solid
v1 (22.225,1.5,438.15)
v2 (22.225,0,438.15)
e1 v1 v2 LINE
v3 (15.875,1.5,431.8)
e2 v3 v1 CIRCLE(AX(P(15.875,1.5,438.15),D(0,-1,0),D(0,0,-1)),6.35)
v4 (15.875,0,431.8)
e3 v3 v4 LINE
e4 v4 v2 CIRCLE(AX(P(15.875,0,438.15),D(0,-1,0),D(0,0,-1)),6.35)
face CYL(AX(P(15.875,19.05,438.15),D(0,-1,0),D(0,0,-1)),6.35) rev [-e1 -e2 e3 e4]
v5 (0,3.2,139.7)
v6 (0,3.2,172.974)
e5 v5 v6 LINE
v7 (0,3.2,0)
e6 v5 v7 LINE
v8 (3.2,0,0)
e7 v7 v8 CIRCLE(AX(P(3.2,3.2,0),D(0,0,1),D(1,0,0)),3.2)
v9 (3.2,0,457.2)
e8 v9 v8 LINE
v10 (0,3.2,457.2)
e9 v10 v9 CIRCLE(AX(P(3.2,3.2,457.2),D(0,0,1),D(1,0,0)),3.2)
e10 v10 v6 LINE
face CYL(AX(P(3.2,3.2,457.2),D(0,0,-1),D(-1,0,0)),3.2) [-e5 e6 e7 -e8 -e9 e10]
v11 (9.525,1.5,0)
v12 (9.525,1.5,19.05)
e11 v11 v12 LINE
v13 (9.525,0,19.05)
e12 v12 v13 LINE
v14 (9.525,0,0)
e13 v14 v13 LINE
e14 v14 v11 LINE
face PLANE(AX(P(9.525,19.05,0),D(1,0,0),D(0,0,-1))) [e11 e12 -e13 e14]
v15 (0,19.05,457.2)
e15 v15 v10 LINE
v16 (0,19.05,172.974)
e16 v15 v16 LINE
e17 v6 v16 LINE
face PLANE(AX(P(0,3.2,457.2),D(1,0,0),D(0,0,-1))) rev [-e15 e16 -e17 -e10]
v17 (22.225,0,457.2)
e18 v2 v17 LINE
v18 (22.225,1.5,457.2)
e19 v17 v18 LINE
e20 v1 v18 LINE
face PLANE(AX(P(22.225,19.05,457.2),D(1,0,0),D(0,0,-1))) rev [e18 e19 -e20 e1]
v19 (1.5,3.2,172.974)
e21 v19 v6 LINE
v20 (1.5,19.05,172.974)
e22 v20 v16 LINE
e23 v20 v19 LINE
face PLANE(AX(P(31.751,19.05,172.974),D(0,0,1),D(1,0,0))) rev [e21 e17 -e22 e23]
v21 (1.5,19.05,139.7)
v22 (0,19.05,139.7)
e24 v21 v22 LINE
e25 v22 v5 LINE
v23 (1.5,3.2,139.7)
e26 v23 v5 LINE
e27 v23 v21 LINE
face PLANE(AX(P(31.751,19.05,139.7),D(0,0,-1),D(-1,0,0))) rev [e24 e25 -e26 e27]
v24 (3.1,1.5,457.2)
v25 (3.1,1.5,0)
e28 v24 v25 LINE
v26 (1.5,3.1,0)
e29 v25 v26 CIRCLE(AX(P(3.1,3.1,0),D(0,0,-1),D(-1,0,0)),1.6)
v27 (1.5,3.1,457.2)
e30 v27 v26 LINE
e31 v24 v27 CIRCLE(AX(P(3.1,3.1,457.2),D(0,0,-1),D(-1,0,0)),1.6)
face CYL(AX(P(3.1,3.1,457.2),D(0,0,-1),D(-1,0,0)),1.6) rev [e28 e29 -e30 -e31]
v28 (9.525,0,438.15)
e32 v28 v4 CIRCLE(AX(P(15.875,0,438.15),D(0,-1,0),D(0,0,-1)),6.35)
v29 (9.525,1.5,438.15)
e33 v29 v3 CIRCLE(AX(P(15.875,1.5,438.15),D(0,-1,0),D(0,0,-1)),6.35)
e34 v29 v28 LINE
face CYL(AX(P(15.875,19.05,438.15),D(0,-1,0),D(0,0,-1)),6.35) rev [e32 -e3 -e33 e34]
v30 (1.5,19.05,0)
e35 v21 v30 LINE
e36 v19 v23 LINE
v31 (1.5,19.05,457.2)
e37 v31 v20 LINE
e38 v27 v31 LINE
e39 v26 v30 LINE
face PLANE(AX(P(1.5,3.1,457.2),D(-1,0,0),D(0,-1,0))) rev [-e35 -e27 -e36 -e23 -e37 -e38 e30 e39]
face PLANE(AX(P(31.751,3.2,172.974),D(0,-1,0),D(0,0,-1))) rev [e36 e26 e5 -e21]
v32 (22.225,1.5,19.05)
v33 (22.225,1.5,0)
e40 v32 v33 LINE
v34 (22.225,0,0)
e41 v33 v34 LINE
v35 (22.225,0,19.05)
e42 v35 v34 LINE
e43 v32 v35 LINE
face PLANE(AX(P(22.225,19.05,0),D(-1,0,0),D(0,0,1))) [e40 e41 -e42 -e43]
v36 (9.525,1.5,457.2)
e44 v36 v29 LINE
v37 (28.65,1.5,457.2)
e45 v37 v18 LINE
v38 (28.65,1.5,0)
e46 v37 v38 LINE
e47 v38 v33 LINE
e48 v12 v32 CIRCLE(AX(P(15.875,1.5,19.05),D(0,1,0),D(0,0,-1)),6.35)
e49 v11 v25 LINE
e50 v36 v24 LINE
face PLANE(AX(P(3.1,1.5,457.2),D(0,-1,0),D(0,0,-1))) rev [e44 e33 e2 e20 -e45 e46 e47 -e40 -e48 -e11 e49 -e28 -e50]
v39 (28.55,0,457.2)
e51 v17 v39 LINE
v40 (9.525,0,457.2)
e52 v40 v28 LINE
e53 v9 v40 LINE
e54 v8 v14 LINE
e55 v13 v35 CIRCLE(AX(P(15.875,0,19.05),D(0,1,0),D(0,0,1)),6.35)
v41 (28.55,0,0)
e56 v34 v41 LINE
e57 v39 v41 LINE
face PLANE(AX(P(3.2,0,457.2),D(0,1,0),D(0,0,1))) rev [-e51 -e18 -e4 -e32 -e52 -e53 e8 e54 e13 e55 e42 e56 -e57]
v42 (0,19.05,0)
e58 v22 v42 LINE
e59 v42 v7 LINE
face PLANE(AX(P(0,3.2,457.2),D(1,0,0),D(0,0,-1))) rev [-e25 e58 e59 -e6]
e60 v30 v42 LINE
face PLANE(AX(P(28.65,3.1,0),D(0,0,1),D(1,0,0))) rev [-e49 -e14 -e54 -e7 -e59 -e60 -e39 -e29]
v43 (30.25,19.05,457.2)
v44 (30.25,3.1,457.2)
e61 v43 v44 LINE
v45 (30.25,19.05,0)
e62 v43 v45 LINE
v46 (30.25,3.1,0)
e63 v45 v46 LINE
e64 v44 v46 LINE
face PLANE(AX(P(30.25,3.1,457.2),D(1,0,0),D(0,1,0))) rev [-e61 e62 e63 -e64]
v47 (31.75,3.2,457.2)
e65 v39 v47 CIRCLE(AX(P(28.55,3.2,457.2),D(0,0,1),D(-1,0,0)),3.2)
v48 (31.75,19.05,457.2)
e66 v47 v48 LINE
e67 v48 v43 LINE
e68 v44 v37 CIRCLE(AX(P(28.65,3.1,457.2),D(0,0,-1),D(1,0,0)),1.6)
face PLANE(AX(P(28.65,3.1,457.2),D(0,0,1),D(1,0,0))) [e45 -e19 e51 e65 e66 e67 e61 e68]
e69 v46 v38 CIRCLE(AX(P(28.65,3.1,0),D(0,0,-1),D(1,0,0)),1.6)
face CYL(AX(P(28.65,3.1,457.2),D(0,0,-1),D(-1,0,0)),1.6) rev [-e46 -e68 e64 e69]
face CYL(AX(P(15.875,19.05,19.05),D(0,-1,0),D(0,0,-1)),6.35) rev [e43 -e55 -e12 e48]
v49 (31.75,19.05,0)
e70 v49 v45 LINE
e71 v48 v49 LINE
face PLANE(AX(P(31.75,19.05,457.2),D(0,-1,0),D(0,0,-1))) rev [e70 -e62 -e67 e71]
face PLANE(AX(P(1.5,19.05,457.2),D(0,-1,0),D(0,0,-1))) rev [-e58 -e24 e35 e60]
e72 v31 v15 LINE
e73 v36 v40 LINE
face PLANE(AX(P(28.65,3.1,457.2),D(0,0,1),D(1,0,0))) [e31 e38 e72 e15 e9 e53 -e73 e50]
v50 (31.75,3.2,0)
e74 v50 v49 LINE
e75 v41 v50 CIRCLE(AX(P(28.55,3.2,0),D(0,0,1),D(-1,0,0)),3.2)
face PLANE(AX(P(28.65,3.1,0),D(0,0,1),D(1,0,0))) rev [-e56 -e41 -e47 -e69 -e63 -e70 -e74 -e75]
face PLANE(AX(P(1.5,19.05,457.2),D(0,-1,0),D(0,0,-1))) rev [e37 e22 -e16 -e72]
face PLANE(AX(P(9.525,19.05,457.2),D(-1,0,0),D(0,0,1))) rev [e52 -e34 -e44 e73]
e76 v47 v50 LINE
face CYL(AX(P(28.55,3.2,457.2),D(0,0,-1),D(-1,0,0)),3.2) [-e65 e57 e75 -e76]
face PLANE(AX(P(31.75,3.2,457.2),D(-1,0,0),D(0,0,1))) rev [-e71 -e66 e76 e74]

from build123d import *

# Parameters (mm, degrees)
BOSS_EXTRUDE1_DEPTH = 457.2
CUT_EXTRUDE1_REACH  = 460.697
SKETCH2_W           = 33.274
SKETCH2_H           = 15.85
CUT_EXTRUDE2_DEPTH  = 459.696855232


with BuildPart() as part:
    # Sketch1 → Boss-Extrude1 (new body)
    with BuildSketch(Plane.XY):
        with BuildLine():
            Line((30.25, 3.1), (30.25, 19.05))
            Line((30.25, 19.05), (31.75, 19.05))
            Line((31.75, 19.05), (31.75, 3.2))
            ThreePointArc((31.75, 3.2), (30.8127417, 0.9372583), (28.55, 0))
            Line((28.55, 0), (3.2, 0))
            ThreePointArc((3.2, 0), (0.9372583, 0.9372583), (0, 3.2))
            Line((0, 3.2), (0, 19.05))
            Line((0, 19.05), (1.5, 19.05))
            Line((1.5, 19.05), (1.5, 3.1))
            ThreePointArc((1.5, 3.1), (1.96862915, 1.96862915), (3.1, 1.5))
            Line((3.1, 1.5), (28.65, 1.5))
            ThreePointArc((28.65, 1.5), (29.78137085, 1.96862915), (30.25, 3.1))
        make_face()
    extrude(amount=BOSS_EXTRUDE1_DEPTH)

    # Sketch2 → Cut-Extrude1 (cut, up to next)
    with BuildSketch(Plane.ZY, mode=Mode.PRIVATE) as cut_extrude1_sk1:
        with Locations((156.337, 11.125)):
            Rectangle(SKETCH2_W, SKETCH2_H)
    cut_extrude1_tool1 = extrude(cut_extrude1_sk1.sketch, amount=-CUT_EXTRUDE1_REACH, mode=Mode.PRIVATE) & part.part
    add(cut_extrude1_tool1.solids().sort_by_distance((0, 11.125, 156.337))[0], mode=Mode.SUBTRACT)

    # Sketch4 → Cut-Extrude2 (cut, through all)
    with BuildSketch(Plane.XZ):
        with BuildLine():
            Line((9.525, 457.2), (9.525, 438.15))
            ThreePointArc((9.525, 438.15), (15.875, 431.8), (22.225, 438.15))
            Line((22.225, 438.15), (22.225, 457.2))
            Line((22.225, 457.2), (9.525, 457.2))
        make_face()
    cut_extrude2 = extrude(amount=-CUT_EXTRUDE2_DEPTH, mode=Mode.SUBTRACT)

    # Mirror1: Cut-Extrude2 across plane
    add(cut_extrude2.mirror(Plane.XY.offset(228.6)), mode=Mode.SUBTRACT)


solid = part.part
